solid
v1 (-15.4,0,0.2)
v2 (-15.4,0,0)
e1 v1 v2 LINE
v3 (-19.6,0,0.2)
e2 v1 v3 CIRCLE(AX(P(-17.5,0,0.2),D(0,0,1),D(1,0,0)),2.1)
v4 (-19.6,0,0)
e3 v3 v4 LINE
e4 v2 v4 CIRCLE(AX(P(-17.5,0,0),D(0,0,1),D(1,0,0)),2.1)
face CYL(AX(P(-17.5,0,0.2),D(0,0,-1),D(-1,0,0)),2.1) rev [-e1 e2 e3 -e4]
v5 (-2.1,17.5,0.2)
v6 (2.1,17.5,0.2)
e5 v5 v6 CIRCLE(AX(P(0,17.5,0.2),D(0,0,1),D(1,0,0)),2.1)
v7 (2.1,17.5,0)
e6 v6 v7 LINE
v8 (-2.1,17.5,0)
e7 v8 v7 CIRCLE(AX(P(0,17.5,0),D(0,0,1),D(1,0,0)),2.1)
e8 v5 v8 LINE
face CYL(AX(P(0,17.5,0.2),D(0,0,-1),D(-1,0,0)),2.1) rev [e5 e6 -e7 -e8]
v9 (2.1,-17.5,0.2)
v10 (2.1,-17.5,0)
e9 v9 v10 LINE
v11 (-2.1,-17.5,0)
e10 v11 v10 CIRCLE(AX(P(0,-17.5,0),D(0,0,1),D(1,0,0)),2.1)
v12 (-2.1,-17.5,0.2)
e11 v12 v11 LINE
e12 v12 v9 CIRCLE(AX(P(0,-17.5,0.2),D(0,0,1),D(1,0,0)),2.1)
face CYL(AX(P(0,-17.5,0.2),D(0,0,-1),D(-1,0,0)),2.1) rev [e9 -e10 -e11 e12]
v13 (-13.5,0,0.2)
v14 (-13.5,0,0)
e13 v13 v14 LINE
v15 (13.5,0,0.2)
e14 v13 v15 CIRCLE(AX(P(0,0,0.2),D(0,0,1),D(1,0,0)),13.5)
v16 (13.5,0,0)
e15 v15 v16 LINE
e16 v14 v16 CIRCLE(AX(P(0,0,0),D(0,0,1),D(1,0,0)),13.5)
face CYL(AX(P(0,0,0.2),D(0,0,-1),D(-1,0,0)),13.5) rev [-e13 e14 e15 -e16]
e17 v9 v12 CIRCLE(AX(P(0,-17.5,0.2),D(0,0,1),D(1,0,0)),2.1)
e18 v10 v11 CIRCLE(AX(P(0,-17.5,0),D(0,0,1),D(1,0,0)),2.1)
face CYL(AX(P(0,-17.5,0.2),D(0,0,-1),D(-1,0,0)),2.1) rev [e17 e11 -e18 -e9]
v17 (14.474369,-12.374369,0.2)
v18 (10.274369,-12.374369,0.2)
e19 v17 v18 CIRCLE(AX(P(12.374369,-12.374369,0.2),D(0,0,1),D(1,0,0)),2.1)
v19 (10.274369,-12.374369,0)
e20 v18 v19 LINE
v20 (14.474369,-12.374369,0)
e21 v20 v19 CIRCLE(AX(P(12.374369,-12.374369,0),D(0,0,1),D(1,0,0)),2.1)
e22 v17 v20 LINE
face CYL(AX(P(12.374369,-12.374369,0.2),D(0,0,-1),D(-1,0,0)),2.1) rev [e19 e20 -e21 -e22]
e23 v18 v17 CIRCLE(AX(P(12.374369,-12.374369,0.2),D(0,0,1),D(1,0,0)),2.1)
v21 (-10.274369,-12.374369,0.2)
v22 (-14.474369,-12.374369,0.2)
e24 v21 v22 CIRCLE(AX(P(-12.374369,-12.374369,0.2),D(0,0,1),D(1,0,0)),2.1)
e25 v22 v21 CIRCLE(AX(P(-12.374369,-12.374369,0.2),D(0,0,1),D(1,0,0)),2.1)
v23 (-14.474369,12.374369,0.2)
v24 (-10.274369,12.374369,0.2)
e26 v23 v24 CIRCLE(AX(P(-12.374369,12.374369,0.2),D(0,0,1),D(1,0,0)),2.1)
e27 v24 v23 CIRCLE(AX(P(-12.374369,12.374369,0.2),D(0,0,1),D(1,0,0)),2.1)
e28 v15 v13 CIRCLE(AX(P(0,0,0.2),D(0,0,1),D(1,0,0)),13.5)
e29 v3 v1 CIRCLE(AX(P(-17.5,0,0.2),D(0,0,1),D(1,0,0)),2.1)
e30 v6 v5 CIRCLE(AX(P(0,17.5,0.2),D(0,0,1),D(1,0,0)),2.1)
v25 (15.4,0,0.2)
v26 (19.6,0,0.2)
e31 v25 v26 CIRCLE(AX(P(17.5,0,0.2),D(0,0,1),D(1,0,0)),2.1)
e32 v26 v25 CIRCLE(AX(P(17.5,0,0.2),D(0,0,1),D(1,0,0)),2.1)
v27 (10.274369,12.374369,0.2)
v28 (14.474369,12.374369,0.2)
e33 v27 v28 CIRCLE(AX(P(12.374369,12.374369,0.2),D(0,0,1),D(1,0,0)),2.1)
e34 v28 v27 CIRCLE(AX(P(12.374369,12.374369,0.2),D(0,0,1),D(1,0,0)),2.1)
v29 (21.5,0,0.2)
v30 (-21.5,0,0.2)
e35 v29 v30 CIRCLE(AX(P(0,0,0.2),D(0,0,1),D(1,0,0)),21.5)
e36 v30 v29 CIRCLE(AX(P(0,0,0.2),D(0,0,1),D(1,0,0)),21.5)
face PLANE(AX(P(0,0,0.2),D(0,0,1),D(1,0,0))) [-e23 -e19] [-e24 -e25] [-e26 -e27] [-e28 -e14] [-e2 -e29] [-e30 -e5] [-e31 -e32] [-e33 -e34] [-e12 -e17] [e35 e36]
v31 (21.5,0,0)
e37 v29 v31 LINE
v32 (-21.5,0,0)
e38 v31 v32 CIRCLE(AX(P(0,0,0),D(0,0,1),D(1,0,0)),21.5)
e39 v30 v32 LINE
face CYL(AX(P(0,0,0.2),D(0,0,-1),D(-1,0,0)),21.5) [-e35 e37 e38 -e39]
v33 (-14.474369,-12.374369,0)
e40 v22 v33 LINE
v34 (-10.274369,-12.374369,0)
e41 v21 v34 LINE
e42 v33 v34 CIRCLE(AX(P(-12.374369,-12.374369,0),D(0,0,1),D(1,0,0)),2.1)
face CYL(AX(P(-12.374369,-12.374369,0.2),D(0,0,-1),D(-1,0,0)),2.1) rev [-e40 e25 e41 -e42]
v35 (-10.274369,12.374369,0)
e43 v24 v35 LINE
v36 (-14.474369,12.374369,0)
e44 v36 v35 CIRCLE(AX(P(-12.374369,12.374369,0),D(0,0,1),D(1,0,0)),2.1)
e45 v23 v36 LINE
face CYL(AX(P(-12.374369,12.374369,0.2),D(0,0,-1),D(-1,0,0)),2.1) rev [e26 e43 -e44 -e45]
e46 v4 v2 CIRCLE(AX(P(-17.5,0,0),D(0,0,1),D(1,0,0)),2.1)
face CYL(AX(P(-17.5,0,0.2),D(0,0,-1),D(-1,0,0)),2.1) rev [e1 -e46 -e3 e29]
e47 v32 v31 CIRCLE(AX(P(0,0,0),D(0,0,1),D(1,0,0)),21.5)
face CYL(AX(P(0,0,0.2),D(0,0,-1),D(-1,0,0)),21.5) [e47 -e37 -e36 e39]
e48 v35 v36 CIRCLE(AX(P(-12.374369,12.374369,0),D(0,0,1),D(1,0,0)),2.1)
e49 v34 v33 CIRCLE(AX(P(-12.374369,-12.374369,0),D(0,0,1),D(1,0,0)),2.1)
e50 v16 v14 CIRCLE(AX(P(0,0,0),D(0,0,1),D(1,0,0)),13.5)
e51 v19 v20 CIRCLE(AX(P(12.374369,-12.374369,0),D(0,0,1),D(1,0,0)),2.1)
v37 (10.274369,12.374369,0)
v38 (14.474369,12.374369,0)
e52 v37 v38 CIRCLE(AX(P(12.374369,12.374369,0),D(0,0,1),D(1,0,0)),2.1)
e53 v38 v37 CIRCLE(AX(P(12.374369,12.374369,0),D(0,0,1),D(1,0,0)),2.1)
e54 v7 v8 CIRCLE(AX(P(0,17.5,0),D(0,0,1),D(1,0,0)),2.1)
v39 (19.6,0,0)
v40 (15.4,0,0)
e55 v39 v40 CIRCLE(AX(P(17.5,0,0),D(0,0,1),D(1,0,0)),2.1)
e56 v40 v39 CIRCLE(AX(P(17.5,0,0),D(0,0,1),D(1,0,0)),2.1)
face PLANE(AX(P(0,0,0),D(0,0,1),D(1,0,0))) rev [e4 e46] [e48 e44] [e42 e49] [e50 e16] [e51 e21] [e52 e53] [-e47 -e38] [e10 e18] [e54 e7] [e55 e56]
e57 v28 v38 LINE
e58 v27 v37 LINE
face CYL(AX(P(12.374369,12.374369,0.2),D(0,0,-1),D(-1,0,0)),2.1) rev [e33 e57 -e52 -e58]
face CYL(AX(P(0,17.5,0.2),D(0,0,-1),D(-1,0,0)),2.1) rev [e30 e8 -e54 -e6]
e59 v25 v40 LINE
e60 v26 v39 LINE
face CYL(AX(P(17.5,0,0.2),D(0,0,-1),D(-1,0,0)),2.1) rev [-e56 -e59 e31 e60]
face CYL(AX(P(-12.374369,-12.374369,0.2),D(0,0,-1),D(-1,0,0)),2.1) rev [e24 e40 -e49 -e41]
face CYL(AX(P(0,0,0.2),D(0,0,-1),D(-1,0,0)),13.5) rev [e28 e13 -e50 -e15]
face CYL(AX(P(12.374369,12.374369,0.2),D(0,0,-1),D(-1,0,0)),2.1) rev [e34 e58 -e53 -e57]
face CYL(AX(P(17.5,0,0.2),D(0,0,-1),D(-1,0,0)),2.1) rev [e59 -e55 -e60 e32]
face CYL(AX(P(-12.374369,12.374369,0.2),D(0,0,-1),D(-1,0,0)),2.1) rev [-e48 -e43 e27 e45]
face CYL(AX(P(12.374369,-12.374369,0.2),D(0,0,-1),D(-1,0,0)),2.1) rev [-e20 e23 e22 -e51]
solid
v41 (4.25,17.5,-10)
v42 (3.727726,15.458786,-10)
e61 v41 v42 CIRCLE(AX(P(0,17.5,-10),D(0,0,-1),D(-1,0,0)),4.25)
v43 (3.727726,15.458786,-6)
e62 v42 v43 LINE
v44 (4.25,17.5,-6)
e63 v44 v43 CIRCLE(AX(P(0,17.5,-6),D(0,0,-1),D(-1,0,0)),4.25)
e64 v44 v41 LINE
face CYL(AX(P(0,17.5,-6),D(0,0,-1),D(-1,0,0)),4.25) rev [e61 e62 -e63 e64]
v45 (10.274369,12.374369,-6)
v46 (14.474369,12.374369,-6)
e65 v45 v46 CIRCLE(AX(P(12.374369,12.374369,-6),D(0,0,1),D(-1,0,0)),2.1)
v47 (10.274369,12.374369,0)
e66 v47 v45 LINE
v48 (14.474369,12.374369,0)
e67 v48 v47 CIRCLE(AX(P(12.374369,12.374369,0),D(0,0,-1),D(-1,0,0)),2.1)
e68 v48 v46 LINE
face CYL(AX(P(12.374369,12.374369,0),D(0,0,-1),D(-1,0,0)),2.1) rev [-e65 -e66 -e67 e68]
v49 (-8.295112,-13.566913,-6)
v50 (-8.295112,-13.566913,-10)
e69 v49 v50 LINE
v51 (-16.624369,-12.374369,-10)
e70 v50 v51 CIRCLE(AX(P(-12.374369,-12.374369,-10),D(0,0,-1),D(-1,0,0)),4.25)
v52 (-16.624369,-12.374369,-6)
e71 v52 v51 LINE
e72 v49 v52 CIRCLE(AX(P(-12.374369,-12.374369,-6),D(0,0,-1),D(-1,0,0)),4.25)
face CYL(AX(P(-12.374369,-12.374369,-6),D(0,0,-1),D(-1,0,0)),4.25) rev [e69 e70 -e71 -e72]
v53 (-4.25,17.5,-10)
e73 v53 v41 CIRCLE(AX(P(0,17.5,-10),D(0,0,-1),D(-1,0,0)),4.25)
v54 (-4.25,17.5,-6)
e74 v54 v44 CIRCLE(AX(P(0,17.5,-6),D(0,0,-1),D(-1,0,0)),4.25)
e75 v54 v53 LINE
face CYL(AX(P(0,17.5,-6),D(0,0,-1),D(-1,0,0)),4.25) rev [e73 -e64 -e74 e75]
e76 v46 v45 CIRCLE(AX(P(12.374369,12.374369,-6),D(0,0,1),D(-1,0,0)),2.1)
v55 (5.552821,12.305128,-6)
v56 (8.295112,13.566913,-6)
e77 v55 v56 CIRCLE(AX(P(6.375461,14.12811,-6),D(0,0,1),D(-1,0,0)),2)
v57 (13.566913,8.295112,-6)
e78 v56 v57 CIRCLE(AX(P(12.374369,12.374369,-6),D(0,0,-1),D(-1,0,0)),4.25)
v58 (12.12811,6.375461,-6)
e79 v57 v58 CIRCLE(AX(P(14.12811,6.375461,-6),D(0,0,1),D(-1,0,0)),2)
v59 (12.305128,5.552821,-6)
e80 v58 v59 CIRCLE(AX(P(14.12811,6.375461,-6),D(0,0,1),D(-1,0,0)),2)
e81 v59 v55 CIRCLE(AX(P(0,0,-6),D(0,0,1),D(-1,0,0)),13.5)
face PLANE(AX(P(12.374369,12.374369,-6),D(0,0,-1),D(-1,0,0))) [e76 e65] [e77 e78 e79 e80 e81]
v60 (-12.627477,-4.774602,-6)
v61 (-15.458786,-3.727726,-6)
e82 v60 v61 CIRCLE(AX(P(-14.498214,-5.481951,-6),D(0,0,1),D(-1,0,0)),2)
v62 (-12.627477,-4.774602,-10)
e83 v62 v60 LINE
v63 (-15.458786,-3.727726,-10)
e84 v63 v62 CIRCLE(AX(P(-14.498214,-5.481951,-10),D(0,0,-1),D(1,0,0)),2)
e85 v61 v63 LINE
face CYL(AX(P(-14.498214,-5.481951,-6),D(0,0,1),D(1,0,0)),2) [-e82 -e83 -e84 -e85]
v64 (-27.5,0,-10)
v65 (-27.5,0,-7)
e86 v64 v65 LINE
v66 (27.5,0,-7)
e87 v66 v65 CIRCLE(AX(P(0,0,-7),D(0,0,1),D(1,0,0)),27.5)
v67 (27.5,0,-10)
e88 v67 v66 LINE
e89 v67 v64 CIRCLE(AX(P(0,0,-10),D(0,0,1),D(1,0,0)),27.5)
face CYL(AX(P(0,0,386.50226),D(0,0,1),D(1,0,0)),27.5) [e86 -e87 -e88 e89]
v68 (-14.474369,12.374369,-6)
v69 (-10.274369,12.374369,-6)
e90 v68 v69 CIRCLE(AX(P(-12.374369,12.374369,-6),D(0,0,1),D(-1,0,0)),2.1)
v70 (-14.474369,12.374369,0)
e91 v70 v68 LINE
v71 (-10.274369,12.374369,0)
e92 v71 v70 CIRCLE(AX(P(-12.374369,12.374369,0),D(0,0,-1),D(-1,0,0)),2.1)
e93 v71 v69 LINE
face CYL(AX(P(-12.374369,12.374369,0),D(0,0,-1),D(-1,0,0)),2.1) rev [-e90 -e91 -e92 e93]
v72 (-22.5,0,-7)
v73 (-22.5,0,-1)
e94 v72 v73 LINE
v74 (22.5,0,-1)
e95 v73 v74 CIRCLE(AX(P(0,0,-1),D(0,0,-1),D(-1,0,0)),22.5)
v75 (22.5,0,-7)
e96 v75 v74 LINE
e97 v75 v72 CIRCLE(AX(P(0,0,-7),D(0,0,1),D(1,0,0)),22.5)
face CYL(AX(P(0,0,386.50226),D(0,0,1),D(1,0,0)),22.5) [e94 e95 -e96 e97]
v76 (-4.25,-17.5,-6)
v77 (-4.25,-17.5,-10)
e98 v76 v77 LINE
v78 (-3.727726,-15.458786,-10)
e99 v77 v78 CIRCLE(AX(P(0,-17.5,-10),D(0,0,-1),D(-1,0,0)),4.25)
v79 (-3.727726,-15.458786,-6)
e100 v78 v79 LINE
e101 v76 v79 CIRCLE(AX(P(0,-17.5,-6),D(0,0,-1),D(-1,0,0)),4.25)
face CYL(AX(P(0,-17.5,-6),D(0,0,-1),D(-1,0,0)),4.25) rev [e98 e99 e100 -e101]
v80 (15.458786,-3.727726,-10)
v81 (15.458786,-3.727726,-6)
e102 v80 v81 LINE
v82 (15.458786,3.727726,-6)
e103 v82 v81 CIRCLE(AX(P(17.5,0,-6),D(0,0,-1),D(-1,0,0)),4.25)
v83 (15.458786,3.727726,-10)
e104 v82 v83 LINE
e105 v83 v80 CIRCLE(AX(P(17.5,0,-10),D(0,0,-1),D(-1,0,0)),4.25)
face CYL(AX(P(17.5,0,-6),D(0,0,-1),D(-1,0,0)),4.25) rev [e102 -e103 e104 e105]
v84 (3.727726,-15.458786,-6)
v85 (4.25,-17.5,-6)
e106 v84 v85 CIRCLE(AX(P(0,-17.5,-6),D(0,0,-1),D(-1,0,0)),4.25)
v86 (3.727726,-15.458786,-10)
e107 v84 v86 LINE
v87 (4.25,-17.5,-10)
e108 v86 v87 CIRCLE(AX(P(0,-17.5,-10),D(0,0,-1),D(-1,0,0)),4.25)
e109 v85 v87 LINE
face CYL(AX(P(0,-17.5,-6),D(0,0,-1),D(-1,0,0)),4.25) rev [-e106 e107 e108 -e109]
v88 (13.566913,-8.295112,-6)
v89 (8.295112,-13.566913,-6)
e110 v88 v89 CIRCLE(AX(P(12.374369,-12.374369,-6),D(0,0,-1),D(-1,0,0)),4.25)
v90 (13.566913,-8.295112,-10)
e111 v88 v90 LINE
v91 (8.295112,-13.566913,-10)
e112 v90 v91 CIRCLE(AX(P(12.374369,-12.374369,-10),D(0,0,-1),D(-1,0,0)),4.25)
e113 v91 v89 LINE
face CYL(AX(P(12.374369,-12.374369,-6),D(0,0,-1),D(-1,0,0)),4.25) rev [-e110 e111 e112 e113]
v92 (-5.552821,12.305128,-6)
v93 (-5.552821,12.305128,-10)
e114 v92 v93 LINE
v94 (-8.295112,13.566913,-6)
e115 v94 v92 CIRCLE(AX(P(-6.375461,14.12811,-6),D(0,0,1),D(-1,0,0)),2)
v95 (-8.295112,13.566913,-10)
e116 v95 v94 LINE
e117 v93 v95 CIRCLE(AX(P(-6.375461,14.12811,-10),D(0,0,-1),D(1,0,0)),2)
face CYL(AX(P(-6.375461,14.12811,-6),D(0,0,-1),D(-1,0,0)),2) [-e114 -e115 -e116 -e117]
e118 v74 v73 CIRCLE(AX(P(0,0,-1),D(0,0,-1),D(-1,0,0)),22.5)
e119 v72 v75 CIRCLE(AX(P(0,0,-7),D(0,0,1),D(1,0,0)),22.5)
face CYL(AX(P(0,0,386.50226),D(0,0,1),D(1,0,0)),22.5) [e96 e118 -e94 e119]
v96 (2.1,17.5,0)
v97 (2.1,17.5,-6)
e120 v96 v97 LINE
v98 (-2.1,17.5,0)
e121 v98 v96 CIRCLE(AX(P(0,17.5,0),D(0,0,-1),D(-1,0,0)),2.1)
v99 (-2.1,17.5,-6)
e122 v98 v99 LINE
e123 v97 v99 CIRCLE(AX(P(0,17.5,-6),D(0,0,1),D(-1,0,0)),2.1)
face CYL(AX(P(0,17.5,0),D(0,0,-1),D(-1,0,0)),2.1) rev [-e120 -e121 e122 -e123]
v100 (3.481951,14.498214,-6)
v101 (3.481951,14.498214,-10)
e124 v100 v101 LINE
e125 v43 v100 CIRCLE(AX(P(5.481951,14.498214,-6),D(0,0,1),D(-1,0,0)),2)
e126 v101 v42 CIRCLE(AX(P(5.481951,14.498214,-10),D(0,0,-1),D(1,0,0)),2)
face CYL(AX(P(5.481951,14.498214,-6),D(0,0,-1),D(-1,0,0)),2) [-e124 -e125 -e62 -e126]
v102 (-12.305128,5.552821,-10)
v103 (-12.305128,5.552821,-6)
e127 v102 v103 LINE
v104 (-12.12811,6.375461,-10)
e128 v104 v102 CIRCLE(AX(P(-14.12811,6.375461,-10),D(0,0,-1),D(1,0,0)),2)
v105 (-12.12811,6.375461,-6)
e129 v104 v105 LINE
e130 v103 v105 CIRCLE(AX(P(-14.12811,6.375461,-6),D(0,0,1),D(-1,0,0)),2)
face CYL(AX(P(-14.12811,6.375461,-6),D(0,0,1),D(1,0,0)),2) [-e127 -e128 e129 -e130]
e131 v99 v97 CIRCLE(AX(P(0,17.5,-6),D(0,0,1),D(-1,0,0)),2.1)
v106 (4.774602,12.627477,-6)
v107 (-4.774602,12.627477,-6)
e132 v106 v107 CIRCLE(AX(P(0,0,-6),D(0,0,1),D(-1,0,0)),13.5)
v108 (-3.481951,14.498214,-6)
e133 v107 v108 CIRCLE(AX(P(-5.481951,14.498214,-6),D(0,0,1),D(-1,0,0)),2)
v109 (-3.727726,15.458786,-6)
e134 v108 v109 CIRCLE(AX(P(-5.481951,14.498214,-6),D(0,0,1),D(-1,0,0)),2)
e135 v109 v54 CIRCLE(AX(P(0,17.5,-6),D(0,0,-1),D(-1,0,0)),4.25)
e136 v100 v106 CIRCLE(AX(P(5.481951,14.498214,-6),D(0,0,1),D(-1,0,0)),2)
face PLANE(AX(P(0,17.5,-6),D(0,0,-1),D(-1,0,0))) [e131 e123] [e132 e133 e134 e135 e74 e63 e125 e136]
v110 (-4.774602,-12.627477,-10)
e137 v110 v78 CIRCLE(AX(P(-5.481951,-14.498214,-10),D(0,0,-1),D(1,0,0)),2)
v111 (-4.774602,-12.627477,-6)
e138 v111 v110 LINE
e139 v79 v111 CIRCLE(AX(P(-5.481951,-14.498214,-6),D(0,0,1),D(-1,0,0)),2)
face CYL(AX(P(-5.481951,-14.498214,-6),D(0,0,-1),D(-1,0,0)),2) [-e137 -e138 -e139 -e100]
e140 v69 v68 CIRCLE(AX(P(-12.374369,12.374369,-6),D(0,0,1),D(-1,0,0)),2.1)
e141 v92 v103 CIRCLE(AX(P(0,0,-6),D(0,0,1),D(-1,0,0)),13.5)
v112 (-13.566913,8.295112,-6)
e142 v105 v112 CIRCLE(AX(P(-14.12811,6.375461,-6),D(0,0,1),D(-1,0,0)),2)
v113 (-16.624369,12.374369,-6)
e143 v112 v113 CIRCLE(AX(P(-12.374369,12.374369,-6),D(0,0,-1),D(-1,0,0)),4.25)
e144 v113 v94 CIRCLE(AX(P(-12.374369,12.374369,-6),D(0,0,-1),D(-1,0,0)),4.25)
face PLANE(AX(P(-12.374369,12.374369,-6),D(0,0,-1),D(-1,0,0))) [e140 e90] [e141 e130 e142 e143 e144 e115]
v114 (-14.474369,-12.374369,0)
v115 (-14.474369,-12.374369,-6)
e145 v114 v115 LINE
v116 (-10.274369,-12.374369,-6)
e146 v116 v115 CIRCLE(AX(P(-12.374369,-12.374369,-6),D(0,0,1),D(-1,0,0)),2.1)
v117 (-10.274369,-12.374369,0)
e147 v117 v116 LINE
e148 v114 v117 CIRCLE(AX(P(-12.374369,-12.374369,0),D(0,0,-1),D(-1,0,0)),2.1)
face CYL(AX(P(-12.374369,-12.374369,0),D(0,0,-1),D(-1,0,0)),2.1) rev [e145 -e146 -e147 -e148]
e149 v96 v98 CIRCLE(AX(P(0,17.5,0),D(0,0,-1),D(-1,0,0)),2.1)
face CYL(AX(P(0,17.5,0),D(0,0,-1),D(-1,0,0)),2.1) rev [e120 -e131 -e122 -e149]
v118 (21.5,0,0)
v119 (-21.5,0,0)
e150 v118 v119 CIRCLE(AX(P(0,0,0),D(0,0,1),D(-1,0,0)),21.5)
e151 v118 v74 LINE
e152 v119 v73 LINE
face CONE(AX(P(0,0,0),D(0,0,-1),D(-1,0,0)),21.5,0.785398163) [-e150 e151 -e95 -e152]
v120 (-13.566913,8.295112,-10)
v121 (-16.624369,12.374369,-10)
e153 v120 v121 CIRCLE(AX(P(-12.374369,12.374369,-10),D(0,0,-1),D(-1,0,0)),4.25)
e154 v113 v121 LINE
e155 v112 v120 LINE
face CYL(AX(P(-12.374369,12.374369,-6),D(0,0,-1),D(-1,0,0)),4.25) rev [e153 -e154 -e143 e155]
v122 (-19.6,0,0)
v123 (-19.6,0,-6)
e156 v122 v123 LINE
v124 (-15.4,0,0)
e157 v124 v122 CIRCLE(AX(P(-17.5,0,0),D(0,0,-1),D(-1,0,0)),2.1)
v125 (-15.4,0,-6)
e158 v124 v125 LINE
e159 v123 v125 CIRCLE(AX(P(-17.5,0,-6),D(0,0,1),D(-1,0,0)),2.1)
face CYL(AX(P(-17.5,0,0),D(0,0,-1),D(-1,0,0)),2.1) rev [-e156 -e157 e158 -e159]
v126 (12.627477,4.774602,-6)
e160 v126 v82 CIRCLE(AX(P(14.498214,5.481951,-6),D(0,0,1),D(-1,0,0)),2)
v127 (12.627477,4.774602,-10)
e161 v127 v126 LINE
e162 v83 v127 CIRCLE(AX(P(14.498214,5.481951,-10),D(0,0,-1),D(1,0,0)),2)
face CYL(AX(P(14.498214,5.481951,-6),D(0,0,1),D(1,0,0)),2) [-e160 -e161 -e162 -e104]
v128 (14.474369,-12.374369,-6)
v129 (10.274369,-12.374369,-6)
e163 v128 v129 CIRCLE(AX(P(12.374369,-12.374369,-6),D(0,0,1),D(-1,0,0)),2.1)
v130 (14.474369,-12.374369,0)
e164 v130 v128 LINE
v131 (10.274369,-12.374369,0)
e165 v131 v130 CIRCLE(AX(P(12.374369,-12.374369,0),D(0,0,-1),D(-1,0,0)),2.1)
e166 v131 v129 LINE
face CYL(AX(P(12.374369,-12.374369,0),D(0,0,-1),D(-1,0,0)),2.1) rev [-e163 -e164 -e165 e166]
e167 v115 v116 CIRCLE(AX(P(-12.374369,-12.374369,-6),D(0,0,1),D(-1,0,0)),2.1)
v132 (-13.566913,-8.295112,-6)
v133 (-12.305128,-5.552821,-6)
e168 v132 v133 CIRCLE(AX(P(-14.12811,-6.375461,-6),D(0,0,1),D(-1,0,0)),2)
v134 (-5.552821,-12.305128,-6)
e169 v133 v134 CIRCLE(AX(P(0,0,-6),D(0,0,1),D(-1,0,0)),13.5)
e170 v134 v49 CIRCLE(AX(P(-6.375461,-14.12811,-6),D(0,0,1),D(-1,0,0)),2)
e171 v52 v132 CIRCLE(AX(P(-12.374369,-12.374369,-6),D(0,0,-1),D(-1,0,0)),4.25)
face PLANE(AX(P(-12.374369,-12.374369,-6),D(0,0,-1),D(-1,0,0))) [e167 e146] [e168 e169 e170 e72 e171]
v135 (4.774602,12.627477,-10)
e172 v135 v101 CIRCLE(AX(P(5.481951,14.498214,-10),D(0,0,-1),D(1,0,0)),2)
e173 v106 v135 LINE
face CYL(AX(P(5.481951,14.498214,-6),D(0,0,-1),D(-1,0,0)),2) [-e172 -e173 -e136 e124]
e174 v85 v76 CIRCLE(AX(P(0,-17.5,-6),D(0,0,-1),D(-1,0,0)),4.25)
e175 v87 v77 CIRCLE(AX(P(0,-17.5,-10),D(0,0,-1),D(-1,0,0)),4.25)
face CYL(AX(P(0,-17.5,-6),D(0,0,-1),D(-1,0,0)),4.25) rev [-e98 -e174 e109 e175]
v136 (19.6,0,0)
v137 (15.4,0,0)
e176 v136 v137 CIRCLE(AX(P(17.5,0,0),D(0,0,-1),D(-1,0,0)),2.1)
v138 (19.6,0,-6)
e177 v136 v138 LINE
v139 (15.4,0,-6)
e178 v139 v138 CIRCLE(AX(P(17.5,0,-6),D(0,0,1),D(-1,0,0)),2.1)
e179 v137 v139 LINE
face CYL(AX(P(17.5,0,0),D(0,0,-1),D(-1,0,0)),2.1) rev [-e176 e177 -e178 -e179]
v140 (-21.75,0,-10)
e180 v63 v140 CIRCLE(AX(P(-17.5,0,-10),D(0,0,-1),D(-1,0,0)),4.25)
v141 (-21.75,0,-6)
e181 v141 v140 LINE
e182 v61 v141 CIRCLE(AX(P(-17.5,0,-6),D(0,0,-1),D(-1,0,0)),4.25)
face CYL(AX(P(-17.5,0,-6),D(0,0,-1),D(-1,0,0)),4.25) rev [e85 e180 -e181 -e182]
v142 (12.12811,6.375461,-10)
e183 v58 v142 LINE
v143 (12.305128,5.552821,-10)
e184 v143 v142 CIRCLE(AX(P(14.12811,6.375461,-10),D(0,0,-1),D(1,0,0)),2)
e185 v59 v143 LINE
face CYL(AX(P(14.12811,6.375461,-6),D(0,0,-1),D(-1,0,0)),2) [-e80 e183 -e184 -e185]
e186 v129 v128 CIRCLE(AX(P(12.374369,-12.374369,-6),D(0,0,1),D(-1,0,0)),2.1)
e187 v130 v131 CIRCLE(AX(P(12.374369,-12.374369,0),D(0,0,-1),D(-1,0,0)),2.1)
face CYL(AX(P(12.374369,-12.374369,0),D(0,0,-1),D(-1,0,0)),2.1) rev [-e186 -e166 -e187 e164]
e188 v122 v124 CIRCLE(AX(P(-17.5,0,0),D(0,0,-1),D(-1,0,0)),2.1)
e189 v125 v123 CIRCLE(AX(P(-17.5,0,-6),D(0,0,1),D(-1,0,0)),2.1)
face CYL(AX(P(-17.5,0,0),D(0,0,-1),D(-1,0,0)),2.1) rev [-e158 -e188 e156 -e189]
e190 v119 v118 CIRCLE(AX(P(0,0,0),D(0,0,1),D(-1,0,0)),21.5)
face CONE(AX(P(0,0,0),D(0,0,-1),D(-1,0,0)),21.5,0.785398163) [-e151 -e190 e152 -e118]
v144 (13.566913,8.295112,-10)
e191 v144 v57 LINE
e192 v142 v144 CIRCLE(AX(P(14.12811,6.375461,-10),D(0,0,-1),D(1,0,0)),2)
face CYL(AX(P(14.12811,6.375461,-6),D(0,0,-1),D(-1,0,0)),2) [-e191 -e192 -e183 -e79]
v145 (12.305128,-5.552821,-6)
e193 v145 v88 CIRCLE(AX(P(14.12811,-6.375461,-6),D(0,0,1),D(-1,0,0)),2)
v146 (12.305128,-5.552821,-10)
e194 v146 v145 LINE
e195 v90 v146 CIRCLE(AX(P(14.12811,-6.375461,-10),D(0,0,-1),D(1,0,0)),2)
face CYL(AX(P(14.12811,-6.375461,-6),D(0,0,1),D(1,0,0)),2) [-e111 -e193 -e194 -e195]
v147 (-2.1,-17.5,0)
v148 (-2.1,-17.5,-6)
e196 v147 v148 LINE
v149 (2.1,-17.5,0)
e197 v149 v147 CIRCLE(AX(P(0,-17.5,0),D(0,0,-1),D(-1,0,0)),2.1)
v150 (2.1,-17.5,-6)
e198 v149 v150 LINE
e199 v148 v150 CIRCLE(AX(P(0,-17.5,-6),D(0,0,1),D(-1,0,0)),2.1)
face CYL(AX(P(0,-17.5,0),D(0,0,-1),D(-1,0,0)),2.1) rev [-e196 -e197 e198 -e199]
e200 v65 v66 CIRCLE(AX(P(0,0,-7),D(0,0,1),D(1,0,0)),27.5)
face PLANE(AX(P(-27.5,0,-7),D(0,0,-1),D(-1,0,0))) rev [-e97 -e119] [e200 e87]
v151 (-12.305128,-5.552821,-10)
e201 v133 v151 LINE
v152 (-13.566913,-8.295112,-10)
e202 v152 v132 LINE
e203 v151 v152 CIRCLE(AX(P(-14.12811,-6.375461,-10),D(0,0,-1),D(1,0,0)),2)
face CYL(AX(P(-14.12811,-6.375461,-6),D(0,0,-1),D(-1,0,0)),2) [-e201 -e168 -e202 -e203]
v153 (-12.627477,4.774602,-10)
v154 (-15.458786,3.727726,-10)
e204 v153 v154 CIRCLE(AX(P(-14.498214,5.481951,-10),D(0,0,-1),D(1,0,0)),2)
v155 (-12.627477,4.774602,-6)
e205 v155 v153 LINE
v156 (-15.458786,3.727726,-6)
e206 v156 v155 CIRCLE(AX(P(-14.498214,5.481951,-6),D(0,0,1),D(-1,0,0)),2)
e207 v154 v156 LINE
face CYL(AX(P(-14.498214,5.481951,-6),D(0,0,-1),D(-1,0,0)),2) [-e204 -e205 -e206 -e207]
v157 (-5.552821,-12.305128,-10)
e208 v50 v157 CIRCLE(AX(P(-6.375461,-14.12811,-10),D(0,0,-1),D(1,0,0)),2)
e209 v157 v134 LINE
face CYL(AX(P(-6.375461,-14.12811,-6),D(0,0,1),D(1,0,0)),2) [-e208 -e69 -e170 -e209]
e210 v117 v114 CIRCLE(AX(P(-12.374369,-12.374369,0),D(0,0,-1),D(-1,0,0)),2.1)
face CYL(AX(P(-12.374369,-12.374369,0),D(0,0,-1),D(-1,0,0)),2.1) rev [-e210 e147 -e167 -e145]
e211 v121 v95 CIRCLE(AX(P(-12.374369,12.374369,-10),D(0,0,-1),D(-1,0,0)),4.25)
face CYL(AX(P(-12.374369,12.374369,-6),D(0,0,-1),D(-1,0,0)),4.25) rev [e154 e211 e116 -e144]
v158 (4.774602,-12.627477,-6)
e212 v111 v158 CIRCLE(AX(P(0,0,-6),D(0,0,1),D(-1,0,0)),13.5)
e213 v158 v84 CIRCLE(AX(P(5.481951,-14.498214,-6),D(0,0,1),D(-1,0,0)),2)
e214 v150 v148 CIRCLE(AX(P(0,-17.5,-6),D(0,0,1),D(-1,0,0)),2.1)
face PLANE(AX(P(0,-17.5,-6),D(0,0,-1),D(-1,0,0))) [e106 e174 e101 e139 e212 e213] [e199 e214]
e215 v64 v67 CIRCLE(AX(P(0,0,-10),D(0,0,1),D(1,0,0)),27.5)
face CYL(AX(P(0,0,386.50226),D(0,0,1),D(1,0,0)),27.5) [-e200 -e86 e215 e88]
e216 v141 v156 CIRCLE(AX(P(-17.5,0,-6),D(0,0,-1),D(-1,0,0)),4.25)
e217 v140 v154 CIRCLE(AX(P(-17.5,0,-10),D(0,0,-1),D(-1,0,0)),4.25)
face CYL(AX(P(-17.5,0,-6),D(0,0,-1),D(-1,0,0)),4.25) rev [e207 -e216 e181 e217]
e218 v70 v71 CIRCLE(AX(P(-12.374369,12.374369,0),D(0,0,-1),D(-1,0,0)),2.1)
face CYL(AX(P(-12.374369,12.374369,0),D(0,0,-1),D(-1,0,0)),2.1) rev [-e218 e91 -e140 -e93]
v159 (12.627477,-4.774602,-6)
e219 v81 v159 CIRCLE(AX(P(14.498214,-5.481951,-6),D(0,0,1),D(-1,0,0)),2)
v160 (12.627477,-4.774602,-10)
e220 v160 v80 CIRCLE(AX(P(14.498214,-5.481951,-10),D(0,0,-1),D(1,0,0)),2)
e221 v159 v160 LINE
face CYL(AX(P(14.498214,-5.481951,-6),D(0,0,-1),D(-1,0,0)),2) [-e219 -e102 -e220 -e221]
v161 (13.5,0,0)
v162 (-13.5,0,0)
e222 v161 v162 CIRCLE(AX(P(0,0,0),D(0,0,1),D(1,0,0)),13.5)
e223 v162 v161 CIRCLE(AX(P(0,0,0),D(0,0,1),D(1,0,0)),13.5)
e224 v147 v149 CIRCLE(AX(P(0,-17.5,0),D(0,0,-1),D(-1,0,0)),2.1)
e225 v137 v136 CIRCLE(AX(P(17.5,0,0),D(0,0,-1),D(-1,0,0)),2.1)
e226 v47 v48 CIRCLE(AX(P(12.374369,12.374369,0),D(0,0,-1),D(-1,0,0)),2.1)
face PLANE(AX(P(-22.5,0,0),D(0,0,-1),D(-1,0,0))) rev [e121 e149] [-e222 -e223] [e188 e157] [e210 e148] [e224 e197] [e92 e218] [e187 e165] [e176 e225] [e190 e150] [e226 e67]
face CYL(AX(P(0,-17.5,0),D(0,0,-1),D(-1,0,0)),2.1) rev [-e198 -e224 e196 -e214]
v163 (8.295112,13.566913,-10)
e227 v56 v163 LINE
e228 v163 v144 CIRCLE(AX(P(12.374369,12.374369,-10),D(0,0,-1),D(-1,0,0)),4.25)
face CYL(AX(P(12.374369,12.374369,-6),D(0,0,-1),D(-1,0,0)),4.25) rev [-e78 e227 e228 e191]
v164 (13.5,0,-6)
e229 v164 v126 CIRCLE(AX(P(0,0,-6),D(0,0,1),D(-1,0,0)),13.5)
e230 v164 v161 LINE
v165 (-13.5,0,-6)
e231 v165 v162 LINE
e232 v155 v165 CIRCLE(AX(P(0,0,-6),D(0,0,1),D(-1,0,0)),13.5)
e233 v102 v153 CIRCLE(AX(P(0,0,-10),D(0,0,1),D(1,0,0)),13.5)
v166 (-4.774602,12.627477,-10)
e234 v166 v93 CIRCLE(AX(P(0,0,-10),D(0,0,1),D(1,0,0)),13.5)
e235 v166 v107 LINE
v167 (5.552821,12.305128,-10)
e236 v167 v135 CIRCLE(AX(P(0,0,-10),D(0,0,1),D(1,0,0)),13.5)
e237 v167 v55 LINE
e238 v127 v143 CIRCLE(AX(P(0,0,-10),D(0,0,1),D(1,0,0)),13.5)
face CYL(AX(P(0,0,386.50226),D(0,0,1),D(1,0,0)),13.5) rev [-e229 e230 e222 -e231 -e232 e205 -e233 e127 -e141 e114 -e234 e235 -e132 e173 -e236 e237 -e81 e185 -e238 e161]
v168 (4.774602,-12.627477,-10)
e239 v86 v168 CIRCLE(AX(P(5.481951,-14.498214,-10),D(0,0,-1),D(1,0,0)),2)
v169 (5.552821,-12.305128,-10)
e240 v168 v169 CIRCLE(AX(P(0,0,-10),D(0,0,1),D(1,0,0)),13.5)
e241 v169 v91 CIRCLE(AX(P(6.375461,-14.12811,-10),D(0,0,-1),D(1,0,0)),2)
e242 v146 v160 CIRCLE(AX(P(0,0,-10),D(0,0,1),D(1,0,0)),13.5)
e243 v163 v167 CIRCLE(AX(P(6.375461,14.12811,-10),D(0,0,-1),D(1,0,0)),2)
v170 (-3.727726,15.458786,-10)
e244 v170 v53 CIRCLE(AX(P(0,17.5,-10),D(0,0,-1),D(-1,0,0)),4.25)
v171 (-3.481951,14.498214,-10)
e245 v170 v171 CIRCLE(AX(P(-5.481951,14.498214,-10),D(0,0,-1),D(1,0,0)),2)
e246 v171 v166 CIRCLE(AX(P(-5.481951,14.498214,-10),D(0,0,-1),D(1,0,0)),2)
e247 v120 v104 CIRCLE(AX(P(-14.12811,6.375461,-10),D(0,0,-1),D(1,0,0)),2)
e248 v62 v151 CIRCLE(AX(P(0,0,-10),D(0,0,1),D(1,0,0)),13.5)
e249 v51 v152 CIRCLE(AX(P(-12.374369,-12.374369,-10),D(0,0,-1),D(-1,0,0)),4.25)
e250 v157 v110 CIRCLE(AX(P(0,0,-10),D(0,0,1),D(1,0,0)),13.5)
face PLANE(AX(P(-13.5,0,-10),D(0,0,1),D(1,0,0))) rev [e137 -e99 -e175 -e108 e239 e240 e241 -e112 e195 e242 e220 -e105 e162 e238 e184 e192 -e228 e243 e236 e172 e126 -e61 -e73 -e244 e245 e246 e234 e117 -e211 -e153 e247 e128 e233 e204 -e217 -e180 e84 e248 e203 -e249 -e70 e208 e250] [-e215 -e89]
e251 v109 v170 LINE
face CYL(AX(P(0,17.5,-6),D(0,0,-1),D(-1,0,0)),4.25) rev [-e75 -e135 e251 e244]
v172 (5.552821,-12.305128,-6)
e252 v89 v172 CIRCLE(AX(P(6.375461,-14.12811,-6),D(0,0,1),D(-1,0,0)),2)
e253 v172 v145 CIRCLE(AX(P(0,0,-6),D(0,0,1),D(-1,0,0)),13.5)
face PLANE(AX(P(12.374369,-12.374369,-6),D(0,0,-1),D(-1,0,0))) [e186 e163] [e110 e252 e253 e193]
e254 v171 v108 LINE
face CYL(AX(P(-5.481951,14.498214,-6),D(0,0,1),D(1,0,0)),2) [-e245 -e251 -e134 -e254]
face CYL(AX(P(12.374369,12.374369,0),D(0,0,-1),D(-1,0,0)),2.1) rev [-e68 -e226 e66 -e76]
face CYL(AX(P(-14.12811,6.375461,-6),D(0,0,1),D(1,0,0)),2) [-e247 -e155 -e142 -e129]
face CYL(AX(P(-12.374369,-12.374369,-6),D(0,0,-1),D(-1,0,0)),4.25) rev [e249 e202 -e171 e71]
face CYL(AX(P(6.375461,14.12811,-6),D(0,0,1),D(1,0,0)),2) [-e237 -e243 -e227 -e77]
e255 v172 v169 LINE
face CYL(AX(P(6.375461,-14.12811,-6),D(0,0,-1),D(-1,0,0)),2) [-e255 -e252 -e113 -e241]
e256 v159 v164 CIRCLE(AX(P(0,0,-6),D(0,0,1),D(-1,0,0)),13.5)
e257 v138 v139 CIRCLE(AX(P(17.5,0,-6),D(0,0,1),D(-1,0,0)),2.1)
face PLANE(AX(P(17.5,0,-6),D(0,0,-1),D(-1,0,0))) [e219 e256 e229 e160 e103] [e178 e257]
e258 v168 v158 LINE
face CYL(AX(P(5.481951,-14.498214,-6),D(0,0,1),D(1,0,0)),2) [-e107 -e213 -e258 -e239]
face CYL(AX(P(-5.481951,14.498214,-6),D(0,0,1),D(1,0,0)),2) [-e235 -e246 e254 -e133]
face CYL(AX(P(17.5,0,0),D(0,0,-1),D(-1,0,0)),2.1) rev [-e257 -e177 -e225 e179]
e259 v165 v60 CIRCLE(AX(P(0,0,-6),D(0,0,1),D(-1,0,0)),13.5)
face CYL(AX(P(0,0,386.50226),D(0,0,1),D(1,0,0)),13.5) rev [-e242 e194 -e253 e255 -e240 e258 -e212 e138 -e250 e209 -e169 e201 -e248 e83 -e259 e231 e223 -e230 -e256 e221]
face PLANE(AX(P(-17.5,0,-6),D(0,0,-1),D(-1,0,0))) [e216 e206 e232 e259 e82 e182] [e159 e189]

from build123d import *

# Parameters (mm, degrees)
SKETCH_2_R          = 2.1
CUT_EXTRUDE_1_DEPTH = 41.155946011
SKETCH_3_R          = 4.25
CUT_EXTRUDE_5_DEPTH = 4
FILLET_1_R          = 2
CHAMFER_2_SIZE      = 1
SKETCH_4_R          = 21.5
SKETCH_4_R_2        = 13.5
SKETCH_4_R_3        = 2.1
EXTRUDE_1_DEPTH     = 0.2


with BuildPart() as part:
    # 草图1 → 旋转1 (revolve)
    with BuildSketch(Plane(origin=(0, 0, 0), x_dir=(1, 0, 0), z_dir=(0, 1, 0)), mode=Mode.PRIVATE) as revolve_1_sk:
        Polygon((-27.5, 10), (-27.5, 7), (-22.5, 7), (-22.5, 0), (-13.5, 0), (-13.5, 10), align=None)
    revolve(revolve_1_sk.sketch.rotate(Axis((0, 0, 386.502260242), (0, 0, -1)), 180), axis=Axis((0, 0, 386.502260242), (0, 0, -1)))

    # 草图2 → 切除-拉伸1 (cut, through all)
    with BuildSketch(Plane(origin=(0, 0, -10), x_dir=(-1, 0, 0), z_dir=(0, 0, -1))):
        with Locations((0, 17.5)):
            Circle(SKETCH_2_R)
        with Locations((12.374368671, 12.374368671)):
            Circle(SKETCH_2_R)
        with Locations((17.5, 0)):
            Circle(SKETCH_2_R)
        with Locations((12.374368671, -12.374368671)):
            Circle(SKETCH_2_R)
        with Locations((0, -17.5)):
            Circle(SKETCH_2_R)
        with Locations((-12.374368671, -12.374368671)):
            Circle(SKETCH_2_R)
        with Locations((-17.5, 0)):
            Circle(SKETCH_2_R)
        with Locations((-12.374368671, 12.374368671)):
            Circle(SKETCH_2_R)
    extrude(amount=-CUT_EXTRUDE_1_DEPTH, mode=Mode.SUBTRACT)

    # 草图3 → 切除-拉伸5 (cut)
    with BuildSketch(Plane(origin=(0, 0, -10), x_dir=(-1, 0, 0), z_dir=(0, 0, -1))):
        with Locations((0, 17.5)):
            Circle(SKETCH_3_R)
        with Locations((12.374368671, 12.374368671)):
            Circle(SKETCH_3_R)
        with Locations((17.5, 0)):
            Circle(SKETCH_3_R)
        with Locations((12.374368671, -12.374368671)):
            Circle(SKETCH_3_R)
        with Locations((0, -17.5)):
            Circle(SKETCH_3_R)
        with Locations((-12.374368671, -12.374368671)):
            Circle(SKETCH_3_R)
        with Locations((-17.5, 0)):
            Circle(SKETCH_3_R)
        with Locations((-12.374368671, 12.374368671)):
            Circle(SKETCH_3_R)
    extrude(amount=-CUT_EXTRUDE_5_DEPTH, mode=Mode.SUBTRACT)

    # 圆角1
    fillet_1_edges = [part.edges().sort_by_distance(p)[0] for p in [
        (1.259999544, 13.441071429, -8),
        (-1.259999544, 13.441071429, -8),
        (-8.613318531, 10.395226976, -8),
        (-10.395226976, 8.613318531, -8),
        (-13.441071429, 1.259999544, -8),
        (-13.441071429, -1.259999544, -8),
        (-10.395226976, -8.613318531, -8),
        (-8.613318531, -10.395226976, -8),
        (-1.259999544, -13.441071429, -8),
        (1.259999544, -13.441071429, -8),
        (8.613318531, -10.395226976, -8),
        (10.395226976, -8.613318531, -8),
        (13.441071429, -1.259999544, -8),
        (13.441071429, 1.259999544, -8),
        (10.395226976, 8.613318531, -8),
        (8.613318531, 10.395226976, -8),
    ]]
    fillet(fillet_1_edges, radius=FILLET_1_R)

    # 倒角2
    chamfer_2_edges = [part.edges().sort_by_distance(p)[0] for p in [
        (-22.5, 0, 0),
    ]]
    chamfer(chamfer_2_edges, length=CHAMFER_2_SIZE)


with BuildPart() as body_2:
    # 草图4 → 凸台-拉伸1 (new body)
    with BuildSketch(Plane.XY):
        Circle(SKETCH_4_R)
        Circle(SKETCH_4_R_2, mode=Mode.SUBTRACT)
        with Locations((-12.374368671, 12.374368671)):
            Circle(SKETCH_4_R_3, mode=Mode.SUBTRACT)
        with Locations((-17.5, 0)):
            Circle(SKETCH_4_R_3, mode=Mode.SUBTRACT)
        with Locations((-12.374368671, -12.374368671)):
            Circle(SKETCH_4_R_3, mode=Mode.SUBTRACT)
        with Locations((0, -17.5)):
            Circle(SKETCH_4_R_3, mode=Mode.SUBTRACT)
        with Locations((12.374368671, -12.374368671)):
            Circle(SKETCH_4_R_3, mode=Mode.SUBTRACT)
        with Locations((17.5, 0)):
            Circle(SKETCH_4_R_3, mode=Mode.SUBTRACT)
        with Locations((12.374368671, 12.374368671)):
            Circle(SKETCH_4_R_3, mode=Mode.SUBTRACT)
        with Locations((0, 17.5)):
            Circle(SKETCH_4_R_3, mode=Mode.SUBTRACT)
    extrude(amount=EXTRUDE_1_DEPTH)


solid = Compound([part.part, body_2.part])
